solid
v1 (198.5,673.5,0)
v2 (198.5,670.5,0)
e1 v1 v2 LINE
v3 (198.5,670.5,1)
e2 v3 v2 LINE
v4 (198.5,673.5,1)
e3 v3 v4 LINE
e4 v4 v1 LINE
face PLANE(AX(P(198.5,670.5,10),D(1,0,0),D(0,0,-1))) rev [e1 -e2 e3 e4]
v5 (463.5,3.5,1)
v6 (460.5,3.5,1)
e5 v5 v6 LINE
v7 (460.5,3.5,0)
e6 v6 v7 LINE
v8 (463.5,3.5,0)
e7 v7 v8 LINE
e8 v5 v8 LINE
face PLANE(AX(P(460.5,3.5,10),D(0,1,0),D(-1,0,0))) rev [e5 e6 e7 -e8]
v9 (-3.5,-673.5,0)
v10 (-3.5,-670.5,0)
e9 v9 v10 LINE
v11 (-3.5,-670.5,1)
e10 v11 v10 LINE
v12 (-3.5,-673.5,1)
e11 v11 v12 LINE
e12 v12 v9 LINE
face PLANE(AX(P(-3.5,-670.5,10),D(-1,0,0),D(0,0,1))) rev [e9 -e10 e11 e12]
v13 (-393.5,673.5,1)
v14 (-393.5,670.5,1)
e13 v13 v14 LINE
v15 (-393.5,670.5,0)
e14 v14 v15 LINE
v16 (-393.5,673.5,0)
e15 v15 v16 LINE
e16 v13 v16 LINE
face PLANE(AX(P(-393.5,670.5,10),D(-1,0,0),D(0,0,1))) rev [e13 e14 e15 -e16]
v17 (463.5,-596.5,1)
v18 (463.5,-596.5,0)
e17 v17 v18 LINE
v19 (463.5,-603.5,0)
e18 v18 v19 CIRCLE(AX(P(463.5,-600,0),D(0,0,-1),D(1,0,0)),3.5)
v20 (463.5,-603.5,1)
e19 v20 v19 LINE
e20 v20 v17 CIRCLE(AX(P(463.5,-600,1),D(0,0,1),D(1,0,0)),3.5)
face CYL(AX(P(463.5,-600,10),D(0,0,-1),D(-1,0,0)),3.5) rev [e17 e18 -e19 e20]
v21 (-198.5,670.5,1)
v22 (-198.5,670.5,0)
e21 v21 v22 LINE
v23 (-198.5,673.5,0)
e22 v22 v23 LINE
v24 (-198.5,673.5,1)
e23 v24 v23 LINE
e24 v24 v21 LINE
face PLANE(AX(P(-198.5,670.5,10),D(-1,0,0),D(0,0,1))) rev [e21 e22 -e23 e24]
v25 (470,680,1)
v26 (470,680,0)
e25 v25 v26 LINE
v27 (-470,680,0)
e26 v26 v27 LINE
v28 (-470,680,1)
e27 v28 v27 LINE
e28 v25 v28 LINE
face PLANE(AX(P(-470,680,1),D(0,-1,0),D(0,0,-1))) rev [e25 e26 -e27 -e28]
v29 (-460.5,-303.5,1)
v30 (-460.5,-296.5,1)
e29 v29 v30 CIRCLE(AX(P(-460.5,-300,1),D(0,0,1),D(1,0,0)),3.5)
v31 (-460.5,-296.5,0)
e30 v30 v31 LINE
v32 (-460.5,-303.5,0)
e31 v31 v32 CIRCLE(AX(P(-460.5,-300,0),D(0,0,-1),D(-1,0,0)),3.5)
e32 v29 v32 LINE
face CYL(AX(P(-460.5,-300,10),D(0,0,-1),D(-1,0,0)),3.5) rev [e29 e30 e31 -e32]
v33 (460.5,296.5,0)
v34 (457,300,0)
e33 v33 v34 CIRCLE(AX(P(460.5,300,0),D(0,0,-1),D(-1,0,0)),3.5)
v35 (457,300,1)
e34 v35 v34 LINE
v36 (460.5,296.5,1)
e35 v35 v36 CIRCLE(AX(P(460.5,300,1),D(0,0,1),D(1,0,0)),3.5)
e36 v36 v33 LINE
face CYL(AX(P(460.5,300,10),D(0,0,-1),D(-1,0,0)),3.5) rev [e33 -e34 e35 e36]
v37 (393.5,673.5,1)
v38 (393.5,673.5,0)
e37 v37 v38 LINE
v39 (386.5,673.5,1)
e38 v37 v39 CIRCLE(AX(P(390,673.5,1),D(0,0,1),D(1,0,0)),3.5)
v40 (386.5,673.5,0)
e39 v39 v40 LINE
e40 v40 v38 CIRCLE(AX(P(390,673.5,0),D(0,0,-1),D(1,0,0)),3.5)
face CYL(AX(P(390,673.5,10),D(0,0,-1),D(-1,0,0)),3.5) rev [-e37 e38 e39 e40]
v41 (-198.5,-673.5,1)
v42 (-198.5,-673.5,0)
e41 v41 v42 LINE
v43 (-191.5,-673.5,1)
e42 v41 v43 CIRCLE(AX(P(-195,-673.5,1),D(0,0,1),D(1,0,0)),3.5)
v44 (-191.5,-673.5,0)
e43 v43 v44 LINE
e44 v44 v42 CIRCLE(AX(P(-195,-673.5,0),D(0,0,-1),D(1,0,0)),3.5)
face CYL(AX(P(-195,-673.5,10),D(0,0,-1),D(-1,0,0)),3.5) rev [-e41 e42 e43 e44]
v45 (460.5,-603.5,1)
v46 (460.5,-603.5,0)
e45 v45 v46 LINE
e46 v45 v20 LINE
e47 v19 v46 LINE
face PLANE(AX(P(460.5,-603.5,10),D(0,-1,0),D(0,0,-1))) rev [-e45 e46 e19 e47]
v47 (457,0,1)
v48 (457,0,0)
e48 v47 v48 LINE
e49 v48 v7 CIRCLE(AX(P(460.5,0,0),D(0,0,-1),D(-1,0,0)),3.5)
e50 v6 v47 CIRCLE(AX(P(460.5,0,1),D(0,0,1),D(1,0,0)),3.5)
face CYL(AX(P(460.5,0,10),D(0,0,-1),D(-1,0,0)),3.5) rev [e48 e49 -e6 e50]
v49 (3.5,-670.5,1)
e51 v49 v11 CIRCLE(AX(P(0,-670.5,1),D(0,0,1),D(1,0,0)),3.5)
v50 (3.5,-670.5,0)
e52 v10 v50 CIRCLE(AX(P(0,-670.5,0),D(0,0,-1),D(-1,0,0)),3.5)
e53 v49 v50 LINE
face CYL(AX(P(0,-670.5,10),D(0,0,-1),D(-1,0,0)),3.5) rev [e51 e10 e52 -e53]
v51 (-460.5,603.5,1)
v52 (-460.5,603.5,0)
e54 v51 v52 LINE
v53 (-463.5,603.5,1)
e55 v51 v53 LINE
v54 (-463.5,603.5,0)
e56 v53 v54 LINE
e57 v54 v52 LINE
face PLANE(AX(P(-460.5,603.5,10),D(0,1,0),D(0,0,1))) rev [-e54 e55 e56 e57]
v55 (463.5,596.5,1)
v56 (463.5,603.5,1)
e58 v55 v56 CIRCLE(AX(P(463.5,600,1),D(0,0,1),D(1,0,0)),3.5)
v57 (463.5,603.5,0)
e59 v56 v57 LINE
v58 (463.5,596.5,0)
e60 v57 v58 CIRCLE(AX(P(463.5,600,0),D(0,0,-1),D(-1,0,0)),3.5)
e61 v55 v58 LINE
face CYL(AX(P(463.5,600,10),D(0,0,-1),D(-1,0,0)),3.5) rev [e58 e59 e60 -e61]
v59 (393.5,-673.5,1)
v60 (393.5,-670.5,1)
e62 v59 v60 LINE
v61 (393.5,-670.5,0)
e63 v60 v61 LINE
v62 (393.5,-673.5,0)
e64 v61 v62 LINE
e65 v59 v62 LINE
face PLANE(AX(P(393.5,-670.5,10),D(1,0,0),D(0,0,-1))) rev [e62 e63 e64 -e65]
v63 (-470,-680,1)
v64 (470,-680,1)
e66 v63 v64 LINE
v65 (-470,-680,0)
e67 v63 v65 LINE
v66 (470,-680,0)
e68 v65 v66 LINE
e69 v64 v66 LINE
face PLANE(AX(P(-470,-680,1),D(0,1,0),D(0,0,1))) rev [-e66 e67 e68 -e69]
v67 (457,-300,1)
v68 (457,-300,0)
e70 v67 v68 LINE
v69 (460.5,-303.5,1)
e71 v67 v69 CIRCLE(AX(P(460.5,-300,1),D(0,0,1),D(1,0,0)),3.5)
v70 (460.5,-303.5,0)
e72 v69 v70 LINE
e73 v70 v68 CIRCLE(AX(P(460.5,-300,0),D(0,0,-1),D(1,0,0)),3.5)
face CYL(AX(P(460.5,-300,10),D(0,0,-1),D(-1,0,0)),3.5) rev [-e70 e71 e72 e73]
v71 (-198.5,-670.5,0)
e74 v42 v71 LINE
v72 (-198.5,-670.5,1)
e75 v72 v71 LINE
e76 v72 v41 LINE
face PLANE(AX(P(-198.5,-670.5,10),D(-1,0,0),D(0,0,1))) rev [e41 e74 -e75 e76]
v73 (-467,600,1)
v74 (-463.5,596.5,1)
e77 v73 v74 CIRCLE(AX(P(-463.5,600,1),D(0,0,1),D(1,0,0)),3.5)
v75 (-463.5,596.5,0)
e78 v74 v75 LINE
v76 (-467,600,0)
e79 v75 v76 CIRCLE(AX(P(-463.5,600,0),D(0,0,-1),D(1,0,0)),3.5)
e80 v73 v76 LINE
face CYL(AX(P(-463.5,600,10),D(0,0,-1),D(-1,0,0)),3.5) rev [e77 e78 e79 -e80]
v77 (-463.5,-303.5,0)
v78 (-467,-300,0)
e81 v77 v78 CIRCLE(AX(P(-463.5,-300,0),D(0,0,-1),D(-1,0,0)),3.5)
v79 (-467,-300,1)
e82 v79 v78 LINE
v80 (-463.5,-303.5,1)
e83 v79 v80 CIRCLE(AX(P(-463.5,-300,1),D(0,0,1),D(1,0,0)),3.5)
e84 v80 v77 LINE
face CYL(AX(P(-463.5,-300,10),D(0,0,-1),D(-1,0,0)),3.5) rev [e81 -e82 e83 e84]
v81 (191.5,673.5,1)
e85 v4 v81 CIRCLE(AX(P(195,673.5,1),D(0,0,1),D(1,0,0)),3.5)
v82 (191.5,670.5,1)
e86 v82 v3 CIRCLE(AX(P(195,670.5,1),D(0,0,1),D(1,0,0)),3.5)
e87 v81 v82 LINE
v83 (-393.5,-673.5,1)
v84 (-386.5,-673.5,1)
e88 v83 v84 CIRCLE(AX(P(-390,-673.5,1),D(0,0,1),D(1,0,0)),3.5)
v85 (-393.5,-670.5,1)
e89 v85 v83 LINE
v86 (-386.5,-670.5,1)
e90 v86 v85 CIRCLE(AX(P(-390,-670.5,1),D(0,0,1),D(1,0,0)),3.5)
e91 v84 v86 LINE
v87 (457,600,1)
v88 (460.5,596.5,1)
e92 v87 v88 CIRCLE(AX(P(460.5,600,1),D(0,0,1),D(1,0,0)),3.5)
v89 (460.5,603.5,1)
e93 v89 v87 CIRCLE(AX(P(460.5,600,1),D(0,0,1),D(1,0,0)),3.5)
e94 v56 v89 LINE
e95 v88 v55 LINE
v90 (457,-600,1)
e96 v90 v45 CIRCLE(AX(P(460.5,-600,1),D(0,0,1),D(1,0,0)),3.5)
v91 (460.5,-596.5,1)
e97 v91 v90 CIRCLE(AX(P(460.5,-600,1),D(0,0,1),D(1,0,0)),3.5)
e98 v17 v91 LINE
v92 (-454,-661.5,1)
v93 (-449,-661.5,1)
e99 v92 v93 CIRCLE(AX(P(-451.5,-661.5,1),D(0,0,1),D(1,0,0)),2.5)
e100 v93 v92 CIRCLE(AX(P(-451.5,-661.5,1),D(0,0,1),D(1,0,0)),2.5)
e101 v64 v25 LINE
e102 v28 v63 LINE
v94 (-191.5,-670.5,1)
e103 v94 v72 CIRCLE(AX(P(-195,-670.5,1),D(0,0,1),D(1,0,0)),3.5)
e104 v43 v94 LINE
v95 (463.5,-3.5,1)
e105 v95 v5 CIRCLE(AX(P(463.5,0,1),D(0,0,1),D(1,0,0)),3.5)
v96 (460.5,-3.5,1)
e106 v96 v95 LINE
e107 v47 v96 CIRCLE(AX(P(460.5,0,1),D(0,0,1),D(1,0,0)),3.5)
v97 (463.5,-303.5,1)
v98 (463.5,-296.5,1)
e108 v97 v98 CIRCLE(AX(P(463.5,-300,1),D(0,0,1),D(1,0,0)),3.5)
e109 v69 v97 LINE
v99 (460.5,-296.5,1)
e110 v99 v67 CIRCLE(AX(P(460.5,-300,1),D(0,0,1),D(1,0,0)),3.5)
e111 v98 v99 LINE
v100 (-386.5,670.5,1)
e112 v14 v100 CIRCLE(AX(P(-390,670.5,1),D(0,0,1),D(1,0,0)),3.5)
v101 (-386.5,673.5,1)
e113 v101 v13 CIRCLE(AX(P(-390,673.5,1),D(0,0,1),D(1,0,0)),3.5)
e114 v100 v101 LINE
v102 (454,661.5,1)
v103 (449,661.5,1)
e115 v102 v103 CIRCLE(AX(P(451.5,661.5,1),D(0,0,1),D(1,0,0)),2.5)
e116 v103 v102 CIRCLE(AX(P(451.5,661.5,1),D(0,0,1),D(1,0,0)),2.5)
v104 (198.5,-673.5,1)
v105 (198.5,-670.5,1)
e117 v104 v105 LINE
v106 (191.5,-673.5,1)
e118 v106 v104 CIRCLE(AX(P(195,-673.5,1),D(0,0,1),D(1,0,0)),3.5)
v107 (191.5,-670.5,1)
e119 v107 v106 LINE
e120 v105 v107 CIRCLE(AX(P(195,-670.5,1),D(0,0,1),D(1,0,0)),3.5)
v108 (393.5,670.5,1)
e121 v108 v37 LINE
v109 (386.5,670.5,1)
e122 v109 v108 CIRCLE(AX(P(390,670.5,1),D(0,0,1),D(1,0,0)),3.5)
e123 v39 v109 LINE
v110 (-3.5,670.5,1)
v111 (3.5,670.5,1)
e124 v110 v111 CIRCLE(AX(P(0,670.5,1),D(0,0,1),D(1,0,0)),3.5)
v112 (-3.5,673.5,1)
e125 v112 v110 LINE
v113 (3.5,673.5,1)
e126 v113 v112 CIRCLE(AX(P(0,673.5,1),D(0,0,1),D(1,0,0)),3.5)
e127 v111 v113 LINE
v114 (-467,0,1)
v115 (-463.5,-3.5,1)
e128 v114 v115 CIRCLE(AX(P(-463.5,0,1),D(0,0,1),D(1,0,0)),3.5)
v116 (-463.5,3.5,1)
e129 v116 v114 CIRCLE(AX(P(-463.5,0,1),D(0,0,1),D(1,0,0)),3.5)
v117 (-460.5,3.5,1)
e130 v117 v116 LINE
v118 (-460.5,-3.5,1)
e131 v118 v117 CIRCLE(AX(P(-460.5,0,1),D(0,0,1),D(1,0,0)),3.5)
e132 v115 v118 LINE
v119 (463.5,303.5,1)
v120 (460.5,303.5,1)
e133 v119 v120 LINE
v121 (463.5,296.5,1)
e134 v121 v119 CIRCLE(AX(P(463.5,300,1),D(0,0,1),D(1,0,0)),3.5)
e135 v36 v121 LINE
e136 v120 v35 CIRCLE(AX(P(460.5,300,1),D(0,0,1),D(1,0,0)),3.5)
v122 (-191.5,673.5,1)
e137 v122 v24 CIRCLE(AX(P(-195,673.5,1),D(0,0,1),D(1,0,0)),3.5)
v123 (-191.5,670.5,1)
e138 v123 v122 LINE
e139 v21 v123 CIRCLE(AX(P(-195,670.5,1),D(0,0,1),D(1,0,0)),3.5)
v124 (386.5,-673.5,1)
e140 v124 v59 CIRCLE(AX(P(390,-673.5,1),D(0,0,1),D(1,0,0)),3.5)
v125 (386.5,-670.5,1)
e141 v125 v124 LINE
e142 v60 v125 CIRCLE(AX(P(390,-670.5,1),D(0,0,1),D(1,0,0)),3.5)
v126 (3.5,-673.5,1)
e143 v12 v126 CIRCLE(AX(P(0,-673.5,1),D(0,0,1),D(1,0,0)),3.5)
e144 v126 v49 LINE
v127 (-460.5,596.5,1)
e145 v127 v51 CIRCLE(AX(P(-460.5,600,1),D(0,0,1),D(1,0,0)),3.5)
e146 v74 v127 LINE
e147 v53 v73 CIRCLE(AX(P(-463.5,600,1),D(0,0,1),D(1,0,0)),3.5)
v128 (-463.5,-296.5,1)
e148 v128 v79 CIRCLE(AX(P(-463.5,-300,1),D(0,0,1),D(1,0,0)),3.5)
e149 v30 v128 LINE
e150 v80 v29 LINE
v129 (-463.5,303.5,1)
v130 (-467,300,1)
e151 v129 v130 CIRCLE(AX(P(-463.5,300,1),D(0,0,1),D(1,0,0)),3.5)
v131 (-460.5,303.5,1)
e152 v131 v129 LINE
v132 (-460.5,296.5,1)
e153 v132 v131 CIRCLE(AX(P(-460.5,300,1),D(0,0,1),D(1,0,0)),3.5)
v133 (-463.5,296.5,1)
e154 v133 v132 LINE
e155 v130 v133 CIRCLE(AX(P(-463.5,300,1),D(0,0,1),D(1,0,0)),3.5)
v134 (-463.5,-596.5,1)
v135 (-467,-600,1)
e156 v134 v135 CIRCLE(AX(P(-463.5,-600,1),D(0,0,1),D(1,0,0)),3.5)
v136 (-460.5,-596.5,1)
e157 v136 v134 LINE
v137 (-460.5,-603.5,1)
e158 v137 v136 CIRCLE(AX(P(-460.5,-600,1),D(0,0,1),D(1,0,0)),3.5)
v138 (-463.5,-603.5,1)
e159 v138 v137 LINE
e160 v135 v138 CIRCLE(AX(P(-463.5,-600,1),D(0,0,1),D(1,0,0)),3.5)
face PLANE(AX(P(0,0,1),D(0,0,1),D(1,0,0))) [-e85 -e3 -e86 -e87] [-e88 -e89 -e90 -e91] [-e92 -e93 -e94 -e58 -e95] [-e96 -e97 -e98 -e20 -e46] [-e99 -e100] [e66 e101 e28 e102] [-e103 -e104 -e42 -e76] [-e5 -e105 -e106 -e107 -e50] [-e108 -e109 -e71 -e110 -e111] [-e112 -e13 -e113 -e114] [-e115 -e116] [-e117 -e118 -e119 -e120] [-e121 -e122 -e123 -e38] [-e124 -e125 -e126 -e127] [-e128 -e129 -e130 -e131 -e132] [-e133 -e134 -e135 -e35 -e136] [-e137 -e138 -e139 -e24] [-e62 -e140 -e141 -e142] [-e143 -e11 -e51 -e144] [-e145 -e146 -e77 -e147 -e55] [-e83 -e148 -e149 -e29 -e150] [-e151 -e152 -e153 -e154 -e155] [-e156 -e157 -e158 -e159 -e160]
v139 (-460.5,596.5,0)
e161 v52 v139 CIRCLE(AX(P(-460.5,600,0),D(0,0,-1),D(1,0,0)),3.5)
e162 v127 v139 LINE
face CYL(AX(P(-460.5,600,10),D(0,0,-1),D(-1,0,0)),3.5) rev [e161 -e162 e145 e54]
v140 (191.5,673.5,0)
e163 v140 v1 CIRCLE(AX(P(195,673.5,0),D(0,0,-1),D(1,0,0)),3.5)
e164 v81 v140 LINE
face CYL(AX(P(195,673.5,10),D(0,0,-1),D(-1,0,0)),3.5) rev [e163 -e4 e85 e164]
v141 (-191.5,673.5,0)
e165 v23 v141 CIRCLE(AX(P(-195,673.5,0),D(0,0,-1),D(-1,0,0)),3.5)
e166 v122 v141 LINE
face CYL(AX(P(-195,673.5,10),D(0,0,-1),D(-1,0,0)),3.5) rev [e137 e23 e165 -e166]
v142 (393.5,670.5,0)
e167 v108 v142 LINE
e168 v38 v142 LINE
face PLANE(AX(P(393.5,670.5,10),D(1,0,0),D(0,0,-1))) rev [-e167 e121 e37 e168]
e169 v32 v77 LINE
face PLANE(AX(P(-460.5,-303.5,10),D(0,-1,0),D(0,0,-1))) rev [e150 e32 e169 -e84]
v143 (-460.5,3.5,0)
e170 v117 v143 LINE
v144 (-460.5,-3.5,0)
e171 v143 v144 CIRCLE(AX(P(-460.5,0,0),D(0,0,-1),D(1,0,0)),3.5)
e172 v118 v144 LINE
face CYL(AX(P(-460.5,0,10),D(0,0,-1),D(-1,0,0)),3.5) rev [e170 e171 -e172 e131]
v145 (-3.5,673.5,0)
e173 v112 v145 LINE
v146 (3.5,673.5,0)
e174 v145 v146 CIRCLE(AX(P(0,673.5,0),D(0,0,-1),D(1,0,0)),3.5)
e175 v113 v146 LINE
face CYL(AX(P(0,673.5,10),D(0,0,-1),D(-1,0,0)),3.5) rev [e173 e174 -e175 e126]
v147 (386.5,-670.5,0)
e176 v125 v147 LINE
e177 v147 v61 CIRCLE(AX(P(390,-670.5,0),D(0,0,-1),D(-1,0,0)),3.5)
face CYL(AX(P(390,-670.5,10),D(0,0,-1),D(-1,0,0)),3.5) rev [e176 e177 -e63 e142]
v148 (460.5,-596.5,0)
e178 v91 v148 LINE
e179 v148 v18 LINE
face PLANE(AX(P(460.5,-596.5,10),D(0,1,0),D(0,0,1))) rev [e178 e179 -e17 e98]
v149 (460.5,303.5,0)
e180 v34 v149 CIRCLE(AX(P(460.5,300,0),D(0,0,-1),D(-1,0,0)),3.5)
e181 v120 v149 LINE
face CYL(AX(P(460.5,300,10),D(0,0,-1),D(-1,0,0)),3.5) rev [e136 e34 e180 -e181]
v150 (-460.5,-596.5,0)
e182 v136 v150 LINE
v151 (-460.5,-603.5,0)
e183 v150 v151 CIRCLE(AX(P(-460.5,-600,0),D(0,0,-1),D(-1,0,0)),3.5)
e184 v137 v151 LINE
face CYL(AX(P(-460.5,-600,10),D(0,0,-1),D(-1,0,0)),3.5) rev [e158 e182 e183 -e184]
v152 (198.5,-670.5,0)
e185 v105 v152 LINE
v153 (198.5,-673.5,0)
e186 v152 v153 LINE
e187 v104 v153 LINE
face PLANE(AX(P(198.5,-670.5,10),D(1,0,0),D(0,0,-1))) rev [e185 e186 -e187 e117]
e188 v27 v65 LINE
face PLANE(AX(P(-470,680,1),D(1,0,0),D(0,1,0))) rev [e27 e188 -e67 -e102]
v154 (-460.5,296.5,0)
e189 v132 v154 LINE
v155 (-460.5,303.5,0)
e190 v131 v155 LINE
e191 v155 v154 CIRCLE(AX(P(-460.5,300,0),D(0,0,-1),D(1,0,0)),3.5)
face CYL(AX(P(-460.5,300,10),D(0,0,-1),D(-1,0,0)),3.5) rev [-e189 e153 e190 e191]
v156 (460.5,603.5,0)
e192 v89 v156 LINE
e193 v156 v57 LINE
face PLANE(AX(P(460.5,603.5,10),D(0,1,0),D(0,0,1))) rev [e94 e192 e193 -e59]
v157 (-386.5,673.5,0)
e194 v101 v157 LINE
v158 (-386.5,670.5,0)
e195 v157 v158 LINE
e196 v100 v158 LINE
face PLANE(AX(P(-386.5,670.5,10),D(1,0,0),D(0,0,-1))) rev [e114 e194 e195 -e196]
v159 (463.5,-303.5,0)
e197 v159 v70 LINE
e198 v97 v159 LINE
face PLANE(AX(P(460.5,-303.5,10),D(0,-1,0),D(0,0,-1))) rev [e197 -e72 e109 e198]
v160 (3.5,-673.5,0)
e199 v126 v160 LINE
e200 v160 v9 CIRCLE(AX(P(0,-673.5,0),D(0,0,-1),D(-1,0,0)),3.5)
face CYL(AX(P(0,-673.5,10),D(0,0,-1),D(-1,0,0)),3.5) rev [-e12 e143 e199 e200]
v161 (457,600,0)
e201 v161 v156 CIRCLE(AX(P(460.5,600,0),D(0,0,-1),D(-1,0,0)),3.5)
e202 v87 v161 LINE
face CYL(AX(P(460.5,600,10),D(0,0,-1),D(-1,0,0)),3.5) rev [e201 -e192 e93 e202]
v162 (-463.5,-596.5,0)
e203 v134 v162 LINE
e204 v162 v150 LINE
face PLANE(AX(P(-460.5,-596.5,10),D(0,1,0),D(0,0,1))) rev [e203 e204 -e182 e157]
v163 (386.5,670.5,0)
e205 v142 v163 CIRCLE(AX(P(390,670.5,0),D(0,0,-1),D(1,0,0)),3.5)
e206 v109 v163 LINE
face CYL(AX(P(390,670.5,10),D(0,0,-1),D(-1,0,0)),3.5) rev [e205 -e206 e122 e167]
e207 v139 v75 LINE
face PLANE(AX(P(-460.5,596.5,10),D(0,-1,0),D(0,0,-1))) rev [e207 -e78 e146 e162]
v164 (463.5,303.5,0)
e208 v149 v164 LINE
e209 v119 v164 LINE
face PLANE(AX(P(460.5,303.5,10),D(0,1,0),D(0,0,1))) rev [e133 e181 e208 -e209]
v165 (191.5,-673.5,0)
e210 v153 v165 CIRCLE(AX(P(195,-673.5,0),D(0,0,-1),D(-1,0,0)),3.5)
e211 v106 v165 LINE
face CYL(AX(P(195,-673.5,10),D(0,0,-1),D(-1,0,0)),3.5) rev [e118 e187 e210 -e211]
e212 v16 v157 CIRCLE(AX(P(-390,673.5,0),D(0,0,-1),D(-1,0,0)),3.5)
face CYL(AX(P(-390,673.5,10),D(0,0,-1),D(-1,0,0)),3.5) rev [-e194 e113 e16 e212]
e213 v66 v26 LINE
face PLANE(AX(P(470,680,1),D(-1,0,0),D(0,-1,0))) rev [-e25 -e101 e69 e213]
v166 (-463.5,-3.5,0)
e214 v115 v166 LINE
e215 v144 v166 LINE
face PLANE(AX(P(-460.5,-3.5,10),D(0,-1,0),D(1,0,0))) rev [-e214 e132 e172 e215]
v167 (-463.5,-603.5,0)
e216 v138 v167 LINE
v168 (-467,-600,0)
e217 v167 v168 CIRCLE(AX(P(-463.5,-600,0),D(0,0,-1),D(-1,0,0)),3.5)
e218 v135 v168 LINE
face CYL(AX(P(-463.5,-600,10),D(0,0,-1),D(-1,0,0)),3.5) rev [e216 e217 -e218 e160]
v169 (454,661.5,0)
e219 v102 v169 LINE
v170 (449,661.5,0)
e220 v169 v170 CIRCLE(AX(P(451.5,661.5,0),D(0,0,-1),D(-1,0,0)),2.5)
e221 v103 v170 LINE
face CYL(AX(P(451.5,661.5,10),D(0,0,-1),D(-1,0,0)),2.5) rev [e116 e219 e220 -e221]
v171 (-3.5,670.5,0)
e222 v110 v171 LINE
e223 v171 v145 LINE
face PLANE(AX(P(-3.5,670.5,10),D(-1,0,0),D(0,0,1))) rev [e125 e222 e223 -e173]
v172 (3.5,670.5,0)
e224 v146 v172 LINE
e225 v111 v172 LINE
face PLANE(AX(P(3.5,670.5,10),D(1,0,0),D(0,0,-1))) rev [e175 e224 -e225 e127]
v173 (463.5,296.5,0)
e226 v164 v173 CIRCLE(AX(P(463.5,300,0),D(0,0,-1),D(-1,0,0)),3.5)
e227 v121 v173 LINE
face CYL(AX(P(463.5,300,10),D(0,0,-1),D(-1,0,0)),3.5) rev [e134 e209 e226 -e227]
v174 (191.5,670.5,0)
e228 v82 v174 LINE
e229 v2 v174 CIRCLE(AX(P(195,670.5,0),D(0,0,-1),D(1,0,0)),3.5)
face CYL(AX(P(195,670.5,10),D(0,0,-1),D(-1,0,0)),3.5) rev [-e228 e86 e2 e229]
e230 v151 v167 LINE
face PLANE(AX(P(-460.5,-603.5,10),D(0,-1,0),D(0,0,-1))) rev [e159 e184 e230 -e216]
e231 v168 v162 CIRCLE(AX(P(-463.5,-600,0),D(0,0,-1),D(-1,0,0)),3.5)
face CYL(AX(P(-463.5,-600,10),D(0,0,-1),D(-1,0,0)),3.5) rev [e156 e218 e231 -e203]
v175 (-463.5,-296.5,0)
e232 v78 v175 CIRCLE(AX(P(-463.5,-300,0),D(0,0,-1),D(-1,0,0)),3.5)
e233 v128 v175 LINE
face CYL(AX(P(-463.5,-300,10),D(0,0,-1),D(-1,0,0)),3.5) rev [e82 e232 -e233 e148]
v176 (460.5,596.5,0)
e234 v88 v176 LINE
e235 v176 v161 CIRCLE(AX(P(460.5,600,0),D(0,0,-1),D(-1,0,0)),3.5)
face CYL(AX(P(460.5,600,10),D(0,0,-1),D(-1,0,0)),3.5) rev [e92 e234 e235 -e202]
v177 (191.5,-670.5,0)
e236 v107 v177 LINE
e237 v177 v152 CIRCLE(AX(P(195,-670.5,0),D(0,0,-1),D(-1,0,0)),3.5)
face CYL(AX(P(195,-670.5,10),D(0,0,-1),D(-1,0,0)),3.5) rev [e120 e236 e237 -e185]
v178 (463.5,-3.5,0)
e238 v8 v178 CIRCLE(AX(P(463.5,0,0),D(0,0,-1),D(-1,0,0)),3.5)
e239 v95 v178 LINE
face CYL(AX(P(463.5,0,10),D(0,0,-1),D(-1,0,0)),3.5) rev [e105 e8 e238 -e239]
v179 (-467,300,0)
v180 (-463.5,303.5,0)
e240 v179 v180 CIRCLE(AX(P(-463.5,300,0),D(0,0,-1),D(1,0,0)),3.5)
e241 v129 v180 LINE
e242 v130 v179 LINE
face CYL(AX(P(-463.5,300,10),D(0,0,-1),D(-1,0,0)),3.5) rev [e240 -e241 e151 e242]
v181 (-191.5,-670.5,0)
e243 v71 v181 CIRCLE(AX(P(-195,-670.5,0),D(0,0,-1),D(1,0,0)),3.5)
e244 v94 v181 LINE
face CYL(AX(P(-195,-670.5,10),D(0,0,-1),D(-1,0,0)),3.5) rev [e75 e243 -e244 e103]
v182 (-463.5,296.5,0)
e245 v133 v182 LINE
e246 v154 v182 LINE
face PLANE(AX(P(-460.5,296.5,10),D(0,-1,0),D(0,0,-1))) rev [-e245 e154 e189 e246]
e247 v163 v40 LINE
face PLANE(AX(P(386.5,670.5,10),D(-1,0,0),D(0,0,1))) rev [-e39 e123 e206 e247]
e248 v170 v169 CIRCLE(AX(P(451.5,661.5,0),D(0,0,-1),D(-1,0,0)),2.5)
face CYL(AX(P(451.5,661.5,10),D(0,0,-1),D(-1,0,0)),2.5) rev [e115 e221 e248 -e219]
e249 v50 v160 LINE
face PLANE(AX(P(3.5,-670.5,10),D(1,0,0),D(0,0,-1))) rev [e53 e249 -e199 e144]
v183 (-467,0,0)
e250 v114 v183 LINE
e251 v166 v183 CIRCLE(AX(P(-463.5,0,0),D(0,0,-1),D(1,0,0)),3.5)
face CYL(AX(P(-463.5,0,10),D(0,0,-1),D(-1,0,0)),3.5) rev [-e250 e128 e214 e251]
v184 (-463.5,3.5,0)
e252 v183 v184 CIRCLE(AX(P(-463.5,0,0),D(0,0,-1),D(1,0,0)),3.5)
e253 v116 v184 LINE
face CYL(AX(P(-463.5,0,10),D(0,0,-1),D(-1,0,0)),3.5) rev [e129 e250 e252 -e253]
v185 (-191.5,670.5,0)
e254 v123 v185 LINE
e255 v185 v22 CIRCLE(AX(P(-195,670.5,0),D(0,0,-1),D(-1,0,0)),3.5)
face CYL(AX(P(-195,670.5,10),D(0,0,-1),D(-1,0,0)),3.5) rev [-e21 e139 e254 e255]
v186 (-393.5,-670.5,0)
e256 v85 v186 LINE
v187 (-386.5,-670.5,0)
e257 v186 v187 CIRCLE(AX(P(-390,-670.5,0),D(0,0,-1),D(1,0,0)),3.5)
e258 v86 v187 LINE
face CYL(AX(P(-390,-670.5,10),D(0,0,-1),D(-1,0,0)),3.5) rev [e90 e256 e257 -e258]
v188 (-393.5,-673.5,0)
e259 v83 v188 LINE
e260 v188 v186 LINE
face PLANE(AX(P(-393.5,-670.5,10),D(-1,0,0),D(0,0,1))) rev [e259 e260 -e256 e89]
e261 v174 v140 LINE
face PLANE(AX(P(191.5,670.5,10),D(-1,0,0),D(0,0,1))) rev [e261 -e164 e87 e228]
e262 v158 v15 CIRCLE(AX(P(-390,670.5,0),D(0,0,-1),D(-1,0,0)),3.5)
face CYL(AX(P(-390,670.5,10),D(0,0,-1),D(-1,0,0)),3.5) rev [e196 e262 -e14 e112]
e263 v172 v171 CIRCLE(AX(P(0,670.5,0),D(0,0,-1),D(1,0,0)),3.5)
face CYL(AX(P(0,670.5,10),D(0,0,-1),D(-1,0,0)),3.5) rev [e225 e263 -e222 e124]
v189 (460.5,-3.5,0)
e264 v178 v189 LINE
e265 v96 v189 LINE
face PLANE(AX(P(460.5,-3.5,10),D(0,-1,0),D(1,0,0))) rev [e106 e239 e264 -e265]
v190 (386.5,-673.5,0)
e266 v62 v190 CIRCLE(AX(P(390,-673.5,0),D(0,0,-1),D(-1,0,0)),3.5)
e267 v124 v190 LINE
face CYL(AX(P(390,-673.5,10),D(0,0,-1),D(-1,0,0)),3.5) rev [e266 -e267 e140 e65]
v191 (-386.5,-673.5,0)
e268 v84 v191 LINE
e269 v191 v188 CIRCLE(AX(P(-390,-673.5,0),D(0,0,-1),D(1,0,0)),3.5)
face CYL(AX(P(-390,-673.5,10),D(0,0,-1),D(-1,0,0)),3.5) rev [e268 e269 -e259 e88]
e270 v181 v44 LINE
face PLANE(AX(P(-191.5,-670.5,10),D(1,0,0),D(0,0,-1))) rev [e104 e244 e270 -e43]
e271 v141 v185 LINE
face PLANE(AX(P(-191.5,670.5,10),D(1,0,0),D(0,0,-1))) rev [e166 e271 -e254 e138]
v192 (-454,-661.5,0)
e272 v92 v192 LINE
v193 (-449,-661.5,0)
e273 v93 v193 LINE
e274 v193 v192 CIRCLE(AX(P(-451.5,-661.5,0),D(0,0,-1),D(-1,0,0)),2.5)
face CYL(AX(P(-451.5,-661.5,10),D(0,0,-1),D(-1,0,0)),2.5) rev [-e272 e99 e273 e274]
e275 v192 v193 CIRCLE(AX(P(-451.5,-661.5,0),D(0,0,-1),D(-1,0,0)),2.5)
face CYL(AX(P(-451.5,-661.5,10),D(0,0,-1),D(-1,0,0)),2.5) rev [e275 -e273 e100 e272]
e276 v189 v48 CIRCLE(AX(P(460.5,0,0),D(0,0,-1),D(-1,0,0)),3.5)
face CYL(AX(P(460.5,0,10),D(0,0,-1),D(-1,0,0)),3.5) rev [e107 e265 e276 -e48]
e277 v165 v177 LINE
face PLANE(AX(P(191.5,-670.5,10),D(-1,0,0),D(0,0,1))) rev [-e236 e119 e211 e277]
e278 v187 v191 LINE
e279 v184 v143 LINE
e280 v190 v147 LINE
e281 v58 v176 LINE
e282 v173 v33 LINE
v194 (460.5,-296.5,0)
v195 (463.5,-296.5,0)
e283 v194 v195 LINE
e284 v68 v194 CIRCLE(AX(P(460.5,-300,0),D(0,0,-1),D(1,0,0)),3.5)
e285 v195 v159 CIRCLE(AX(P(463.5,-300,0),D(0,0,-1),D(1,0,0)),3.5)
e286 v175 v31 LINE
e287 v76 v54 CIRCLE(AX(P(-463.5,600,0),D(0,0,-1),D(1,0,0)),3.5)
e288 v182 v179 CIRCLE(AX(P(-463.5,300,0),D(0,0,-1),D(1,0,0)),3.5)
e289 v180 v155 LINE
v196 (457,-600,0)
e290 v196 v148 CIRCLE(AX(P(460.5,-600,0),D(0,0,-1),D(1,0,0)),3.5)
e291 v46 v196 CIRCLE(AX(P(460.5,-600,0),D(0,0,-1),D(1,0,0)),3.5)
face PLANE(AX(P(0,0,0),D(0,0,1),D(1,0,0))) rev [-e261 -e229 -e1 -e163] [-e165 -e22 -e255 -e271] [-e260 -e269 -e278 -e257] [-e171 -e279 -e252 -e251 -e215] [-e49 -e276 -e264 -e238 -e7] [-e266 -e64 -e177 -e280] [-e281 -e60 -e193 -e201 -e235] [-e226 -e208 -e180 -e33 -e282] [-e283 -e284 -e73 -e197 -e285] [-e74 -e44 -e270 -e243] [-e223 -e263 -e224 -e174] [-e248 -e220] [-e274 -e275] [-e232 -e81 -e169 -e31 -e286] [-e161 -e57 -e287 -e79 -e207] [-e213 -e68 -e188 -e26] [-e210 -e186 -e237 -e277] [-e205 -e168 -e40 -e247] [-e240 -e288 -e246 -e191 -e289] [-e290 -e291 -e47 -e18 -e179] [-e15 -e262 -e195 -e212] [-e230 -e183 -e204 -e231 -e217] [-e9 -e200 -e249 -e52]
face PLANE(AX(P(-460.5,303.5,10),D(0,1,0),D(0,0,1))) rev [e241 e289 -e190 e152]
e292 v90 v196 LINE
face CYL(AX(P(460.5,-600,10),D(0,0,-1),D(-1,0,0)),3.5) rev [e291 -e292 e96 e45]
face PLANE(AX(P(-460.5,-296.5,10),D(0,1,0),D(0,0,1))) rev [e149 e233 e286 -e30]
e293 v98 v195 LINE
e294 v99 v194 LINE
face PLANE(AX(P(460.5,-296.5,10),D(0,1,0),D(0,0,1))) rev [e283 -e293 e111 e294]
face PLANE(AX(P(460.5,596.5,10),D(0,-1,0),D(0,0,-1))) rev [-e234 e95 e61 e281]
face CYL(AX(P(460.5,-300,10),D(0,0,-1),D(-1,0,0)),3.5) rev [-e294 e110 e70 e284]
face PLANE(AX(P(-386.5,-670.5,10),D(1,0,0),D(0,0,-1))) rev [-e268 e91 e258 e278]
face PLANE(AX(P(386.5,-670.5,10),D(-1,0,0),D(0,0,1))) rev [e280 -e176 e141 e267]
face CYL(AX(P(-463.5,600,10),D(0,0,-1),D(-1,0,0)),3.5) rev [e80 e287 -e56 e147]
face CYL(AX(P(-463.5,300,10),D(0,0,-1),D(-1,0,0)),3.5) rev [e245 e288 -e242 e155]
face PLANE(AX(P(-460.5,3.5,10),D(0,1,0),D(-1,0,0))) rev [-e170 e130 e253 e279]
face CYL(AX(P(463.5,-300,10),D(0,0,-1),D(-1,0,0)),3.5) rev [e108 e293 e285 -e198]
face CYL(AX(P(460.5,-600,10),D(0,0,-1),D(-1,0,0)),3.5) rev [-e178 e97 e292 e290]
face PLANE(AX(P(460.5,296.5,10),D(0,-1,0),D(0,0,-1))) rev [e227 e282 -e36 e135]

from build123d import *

# Parameters (mm, degrees)
SKETCH_1_W          = 940
SKETCH_1_H          = 1360
EXTRUDE_1_DEPTH     = 1
SKETCH_3_R          = 2.5
CUT_EXTRUDE_2_DEPTH = 10
CUT_EXTRUDE_3_DEPTH = 10


with BuildPart() as part:
    # 草图1 → 凸台-拉伸1 (new body)
    with BuildSketch(Plane.XY):
        Rectangle(SKETCH_1_W, SKETCH_1_H)
    extrude(amount=EXTRUDE_1_DEPTH)

    # 草图3 → 切除-拉伸2 (cut)
    with BuildSketch(Plane(origin=(0, 0, 0), x_dir=(-1, 0, 0), z_dir=(0, 0, -1))):
        with Locations((451.5, -661.5)):
            Circle(SKETCH_3_R)
        with Locations((-451.5, 661.5)):
            Circle(SKETCH_3_R)
    extrude(amount=-CUT_EXTRUDE_2_DEPTH, mode=Mode.SUBTRACT)

    # 草图4 → 切除-拉伸3 (cut)
    with BuildSketch(Plane(origin=(0, 0, 0), x_dir=(-1, 0, 0), z_dir=(0, 0, -1))):
        with BuildLine():
            Line((3.5, -670.5), (3.5, -673.5))
            ThreePointArc((3.5, -673.5), (0, -677), (-3.5, -673.5))
            Line((-3.5, -673.5), (-3.5, -670.5))
            ThreePointArc((-3.5, -670.5), (0, -667), (3.5, -670.5))
        make_face()
        with BuildLine():
            Line((-191.5, -670.5), (-191.5, -673.5))
            ThreePointArc((-191.5, -673.5), (-195, -677), (-198.5, -673.5))
            Line((-198.5, -673.5), (-198.5, -670.5))
            ThreePointArc((-198.5, -670.5), (-195, -667), (-191.5, -670.5))
        make_face()
        with BuildLine():
            Line((-386.5, -670.5), (-386.5, -673.5))
            ThreePointArc((-386.5, -673.5), (-390, -677), (-393.5, -673.5))
            Line((-393.5, -673.5), (-393.5, -670.5))
            ThreePointArc((-393.5, -670.5), (-390, -667), (-386.5, -670.5))
        make_face()
        with BuildLine():
            Line((386.5, -670.5), (386.5, -673.5))
            ThreePointArc((386.5, -673.5), (390, -677), (393.5, -673.5))
            Line((393.5, -673.5), (393.5, -670.5))
            ThreePointArc((393.5, -670.5), (390, -667), (386.5, -670.5))
        make_face()
        with BuildLine():
            Line((191.5, -670.5), (191.5, -673.5))
            ThreePointArc((191.5, -673.5), (195, -677), (198.5, -673.5))
            Line((198.5, -673.5), (198.5, -670.5))
            ThreePointArc((198.5, -670.5), (195, -667), (191.5, -670.5))
        make_face()
        with BuildLine():
            Line((-460.5, -3.5), (-463.5, -3.5))
            ThreePointArc((-463.5, -3.5), (-467, 0), (-463.5, 3.5))
            Line((-463.5, 3.5), (-460.5, 3.5))
            ThreePointArc((-460.5, 3.5), (-457, 0), (-460.5, -3.5))
        make_face()
        with BuildLine():
            Line((-460.5, 296.5), (-463.5, 296.5))
            ThreePointArc((-463.5, 296.5), (-467, 300), (-463.5, 303.5))
            Line((-463.5, 303.5), (-460.5, 303.5))
            ThreePointArc((-460.5, 303.5), (-457, 300), (-460.5, 296.5))
        make_face()
        with BuildLine():
            Line((-460.5, 596.5), (-463.5, 596.5))
            ThreePointArc((-463.5, 596.5), (-467, 600), (-463.5, 603.5))
            Line((-463.5, 603.5), (-460.5, 603.5))
            ThreePointArc((-460.5, 603.5), (-457, 600), (-460.5, 596.5))
        make_face()
        with BuildLine():
            Line((-460.5, -596.5), (-463.5, -596.5))
            ThreePointArc((-463.5, -596.5), (-467, -600), (-463.5, -603.5))
            Line((-463.5, -603.5), (-460.5, -603.5))
            ThreePointArc((-460.5, -603.5), (-457, -600), (-460.5, -596.5))
        make_face()
        with BuildLine():
            Line((-460.5, -296.5), (-463.5, -296.5))
            ThreePointArc((-463.5, -296.5), (-467, -300), (-463.5, -303.5))
            Line((-463.5, -303.5), (-460.5, -303.5))
            ThreePointArc((-460.5, -303.5), (-457, -300), (-460.5, -296.5))
        make_face()
        with BuildLine():
            Line((191.5, 670.5), (191.5, 673.5))
            ThreePointArc((191.5, 673.5), (195, 677), (198.5, 673.5))
            Line((198.5, 673.5), (198.5, 670.5))
            ThreePointArc((198.5, 670.5), (195, 667), (191.5, 670.5))
        make_face()
        with BuildLine():
            Line((386.5, 670.5), (386.5, 673.5))
            ThreePointArc((386.5, 673.5), (390, 677), (393.5, 673.5))
            Line((393.5, 673.5), (393.5, 670.5))
            ThreePointArc((393.5, 670.5), (390, 667), (386.5, 670.5))
        make_face()
        with BuildLine():
            Line((-386.5, 670.5), (-386.5, 673.5))
            ThreePointArc((-386.5, 673.5), (-390, 677), (-393.5, 673.5))
            Line((-393.5, 673.5), (-393.5, 670.5))
            ThreePointArc((-393.5, 670.5), (-390, 667), (-386.5, 670.5))
        make_face()
        with BuildLine():
            Line((-191.5, 670.5), (-191.5, 673.5))
            ThreePointArc((-191.5, 673.5), (-195, 677), (-198.5, 673.5))
            Line((-198.5, 673.5), (-198.5, 670.5))
            ThreePointArc((-198.5, 670.5), (-195, 667), (-191.5, 670.5))
        make_face()
        with BuildLine():
            Line((3.5, 670.5), (3.5, 673.5))
            ThreePointArc((3.5, 673.5), (0, 677), (-3.5, 673.5))
            Line((-3.5, 673.5), (-3.5, 670.5))
            ThreePointArc((-3.5, 670.5), (0, 667), (3.5, 670.5))
        make_face()
        with BuildLine():
            Line((460.5, 596.5), (463.5, 596.5))
            ThreePointArc((463.5, 596.5), (467, 600), (463.5, 603.5))
            Line((463.5, 603.5), (460.5, 603.5))
            ThreePointArc((460.5, 603.5), (457, 600), (460.5, 596.5))
        make_face()
        with BuildLine():
            Line((460.5, -296.5), (463.5, -296.5))
            ThreePointArc((463.5, -296.5), (467, -300), (463.5, -303.5))
            Line((463.5, -303.5), (460.5, -303.5))
            ThreePointArc((460.5, -303.5), (457, -300), (460.5, -296.5))
        make_face()
        with BuildLine():
            Line((460.5, -596.5), (463.5, -596.5))
            ThreePointArc((463.5, -596.5), (467, -600), (463.5, -603.5))
            Line((463.5, -603.5), (460.5, -603.5))
            ThreePointArc((460.5, -603.5), (457, -600), (460.5, -596.5))
        make_face()
        with BuildLine():
            Line((460.5, 296.5), (463.5, 296.5))
            ThreePointArc((463.5, 296.5), (467, 300), (463.5, 303.5))
            Line((463.5, 303.5), (460.5, 303.5))
            ThreePointArc((460.5, 303.5), (457, 300), (460.5, 296.5))
        make_face()
        with BuildLine():
            Line((460.5, -3.5), (463.5, -3.5))
            ThreePointArc((463.5, -3.5), (467, 0), (463.5, 3.5))
            Line((463.5, 3.5), (460.5, 3.5))
            ThreePointArc((460.5, 3.5), (457, 0), (460.5, -3.5))
        make_face()
    extrude(amount=-CUT_EXTRUDE_3_DEPTH, mode=Mode.SUBTRACT)


solid = part.part
